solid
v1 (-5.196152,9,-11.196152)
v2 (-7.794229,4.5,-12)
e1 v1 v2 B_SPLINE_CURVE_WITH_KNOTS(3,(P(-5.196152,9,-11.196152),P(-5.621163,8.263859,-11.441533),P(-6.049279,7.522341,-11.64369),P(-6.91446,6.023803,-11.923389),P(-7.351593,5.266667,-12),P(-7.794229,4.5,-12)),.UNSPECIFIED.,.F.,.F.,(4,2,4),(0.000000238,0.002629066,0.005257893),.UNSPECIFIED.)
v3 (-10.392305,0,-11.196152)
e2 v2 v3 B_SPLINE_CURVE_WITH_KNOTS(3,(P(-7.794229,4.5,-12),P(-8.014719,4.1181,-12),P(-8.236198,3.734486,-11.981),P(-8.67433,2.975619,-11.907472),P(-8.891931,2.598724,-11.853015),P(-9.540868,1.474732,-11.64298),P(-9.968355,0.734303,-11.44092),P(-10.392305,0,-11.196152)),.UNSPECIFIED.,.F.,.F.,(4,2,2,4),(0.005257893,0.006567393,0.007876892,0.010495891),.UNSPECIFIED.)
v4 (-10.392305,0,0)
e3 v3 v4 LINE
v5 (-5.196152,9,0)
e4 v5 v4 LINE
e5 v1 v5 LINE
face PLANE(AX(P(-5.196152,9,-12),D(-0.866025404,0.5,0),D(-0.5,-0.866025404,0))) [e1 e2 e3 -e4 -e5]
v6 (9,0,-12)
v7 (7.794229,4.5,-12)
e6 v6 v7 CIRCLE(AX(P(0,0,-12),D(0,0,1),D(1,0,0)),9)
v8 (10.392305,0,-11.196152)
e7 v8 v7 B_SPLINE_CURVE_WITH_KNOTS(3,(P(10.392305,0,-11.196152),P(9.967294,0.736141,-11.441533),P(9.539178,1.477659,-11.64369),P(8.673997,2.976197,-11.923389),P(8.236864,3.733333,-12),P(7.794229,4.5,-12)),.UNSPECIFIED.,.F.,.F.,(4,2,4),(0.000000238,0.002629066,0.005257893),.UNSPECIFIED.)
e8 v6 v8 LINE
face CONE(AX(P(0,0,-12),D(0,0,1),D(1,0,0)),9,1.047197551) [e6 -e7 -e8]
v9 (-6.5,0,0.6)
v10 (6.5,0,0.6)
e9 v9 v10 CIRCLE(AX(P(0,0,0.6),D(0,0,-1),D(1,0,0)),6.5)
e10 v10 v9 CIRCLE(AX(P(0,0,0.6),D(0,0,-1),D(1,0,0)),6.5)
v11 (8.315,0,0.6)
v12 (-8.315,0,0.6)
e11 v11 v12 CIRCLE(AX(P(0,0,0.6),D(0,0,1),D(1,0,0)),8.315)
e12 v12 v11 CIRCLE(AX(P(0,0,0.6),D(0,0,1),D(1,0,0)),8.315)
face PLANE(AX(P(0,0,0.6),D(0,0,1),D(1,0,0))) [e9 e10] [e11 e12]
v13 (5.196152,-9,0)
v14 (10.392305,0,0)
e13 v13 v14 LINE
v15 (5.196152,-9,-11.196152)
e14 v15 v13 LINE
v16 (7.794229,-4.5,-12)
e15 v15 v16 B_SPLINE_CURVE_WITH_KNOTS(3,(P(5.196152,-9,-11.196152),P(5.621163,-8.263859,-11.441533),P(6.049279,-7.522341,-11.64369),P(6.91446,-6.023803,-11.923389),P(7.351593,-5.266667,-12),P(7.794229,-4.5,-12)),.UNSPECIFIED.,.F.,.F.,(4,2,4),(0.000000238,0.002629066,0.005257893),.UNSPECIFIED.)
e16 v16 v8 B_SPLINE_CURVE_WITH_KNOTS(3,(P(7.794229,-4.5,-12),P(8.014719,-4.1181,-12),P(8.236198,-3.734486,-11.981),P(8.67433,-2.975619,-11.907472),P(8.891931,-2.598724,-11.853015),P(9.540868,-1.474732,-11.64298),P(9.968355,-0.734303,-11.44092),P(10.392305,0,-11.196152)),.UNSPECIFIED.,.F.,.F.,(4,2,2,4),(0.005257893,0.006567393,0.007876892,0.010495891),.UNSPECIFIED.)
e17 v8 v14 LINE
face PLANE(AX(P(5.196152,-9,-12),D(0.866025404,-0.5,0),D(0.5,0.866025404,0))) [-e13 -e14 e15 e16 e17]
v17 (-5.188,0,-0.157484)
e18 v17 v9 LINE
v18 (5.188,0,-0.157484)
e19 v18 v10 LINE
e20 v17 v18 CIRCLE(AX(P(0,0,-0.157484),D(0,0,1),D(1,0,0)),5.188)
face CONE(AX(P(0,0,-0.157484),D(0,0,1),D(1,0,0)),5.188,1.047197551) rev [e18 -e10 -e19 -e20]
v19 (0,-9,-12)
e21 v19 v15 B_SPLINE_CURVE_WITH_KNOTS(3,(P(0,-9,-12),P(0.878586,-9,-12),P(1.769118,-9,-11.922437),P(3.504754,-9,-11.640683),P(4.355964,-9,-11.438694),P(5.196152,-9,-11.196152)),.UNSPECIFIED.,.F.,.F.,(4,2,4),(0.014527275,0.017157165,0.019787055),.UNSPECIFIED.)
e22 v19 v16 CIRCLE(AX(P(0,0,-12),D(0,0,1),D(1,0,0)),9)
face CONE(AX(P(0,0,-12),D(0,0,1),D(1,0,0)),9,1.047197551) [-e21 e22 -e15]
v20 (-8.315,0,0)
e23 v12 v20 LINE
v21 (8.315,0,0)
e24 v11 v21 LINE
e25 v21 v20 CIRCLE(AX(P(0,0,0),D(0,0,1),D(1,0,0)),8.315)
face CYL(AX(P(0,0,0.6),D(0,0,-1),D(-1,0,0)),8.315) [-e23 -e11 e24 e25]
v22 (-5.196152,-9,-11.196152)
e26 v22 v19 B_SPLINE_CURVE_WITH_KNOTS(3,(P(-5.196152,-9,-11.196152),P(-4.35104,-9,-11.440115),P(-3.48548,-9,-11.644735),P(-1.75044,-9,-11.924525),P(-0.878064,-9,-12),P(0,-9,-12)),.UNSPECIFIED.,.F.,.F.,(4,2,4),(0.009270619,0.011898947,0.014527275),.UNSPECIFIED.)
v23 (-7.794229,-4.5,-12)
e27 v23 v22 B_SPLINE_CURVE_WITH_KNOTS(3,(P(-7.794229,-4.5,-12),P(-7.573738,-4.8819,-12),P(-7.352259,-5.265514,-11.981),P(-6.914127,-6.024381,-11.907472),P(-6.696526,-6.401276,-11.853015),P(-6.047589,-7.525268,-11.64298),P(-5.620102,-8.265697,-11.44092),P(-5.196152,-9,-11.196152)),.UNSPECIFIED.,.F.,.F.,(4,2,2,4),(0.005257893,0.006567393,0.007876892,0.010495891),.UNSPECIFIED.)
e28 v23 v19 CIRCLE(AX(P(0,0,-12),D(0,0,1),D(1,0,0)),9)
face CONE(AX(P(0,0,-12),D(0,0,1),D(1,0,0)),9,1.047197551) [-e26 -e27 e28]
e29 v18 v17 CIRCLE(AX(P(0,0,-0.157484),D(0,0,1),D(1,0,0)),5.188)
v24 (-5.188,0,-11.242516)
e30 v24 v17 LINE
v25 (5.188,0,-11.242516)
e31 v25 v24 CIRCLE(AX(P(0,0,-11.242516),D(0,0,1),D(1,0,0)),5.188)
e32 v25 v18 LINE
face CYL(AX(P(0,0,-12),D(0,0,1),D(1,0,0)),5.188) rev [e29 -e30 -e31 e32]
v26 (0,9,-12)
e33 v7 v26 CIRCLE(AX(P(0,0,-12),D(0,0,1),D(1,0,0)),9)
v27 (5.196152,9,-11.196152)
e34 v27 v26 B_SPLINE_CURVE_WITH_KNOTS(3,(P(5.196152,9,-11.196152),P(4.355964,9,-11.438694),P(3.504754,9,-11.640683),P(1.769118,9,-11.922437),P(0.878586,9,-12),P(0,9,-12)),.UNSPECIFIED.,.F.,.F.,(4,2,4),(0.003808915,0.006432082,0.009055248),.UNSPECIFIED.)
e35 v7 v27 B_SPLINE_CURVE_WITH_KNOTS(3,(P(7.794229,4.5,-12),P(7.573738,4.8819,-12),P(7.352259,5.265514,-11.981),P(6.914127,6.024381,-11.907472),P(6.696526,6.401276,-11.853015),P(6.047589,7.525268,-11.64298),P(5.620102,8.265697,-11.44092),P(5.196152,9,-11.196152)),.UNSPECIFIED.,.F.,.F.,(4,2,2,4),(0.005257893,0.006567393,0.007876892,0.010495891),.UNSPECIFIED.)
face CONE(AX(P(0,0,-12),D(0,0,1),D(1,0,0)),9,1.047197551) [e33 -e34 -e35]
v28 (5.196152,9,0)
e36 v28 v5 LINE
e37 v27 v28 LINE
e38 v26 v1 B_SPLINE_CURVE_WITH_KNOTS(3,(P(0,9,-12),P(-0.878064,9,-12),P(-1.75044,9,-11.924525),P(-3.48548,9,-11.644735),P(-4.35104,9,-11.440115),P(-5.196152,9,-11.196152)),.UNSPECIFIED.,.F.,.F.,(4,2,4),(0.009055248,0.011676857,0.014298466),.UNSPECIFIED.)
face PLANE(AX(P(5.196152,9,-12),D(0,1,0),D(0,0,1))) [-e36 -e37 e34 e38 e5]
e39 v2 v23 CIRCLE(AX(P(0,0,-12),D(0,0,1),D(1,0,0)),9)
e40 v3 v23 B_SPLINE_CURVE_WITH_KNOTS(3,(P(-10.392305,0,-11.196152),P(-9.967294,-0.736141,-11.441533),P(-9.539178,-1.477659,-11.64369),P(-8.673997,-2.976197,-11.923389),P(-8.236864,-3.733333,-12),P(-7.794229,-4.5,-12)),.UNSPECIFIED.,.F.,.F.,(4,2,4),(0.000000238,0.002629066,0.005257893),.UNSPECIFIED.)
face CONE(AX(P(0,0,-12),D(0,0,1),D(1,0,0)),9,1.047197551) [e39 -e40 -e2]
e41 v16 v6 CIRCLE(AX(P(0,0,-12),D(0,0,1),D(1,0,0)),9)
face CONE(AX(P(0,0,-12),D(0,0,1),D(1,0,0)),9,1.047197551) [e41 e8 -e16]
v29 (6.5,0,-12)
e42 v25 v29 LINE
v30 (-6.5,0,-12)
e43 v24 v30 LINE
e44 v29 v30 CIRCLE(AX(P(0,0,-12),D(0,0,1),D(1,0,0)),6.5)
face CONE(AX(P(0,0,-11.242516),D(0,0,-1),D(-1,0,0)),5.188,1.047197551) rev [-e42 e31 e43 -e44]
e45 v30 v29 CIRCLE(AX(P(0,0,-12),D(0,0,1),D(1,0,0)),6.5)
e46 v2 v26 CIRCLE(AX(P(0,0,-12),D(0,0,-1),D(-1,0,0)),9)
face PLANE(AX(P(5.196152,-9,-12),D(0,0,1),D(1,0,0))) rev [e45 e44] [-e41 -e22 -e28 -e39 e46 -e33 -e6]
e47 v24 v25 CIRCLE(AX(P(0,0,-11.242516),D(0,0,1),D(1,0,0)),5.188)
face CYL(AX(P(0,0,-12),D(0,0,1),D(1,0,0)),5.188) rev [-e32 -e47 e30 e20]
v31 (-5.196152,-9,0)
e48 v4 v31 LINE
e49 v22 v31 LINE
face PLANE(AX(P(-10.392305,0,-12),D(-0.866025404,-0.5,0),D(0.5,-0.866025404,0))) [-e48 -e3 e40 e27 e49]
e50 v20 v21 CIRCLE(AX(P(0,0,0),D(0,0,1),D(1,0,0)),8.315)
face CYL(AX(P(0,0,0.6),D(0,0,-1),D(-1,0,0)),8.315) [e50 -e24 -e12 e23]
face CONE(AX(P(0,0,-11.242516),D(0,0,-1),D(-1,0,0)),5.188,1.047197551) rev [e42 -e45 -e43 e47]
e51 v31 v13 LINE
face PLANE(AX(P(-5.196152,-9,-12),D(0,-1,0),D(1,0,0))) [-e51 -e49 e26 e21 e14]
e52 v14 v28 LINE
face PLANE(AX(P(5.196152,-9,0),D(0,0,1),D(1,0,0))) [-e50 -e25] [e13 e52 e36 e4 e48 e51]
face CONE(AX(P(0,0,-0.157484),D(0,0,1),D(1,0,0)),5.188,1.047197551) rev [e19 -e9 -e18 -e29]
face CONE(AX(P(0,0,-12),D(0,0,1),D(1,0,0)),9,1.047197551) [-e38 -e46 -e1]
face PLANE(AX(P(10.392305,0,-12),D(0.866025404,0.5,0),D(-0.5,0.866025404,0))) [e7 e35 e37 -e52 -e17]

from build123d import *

# Parameters (mm, degrees)
SKETCH1_R         = 5.188
BASENUT_DEPTH     = 12
EXTRUDE1_START    = 0.6
SKETCH3_R         = 8.315
SKETCH3_R_2       = 5.188
EXTRUDE1_DEPTH    = 0.6
ENDCHAMFER3_SIZE  = 1.312
ENDCHAMFER3_SIZE2 = 0.757483553


with BuildPart() as part:
    # Sketch1 → BaseNut (new body)
    with BuildSketch(Plane.XY):
        Polygon((5.196152423, -9), (10.392304845, 0), (5.196152423, 9), (-5.196152423, 9), (-10.392304845, 0), (-5.196152423, -9), align=None)
        Circle(SKETCH1_R, mode=Mode.SUBTRACT)
    extrude(amount=-BASENUT_DEPTH)

    # Sketch2 → Chamfer1 (revolve, cut)
    with BuildSketch(Plane(origin=(-16.706149795, 0, -15.04811501), x_dir=(0, 0, 1), z_dir=(0, 1, 0))):
        Polygon((3.04811501, 25.706149795), (3.04811501, 27.098454641), (3.851962587, 27.098454641), align=None)
    revolve(axis=Axis((0, 0, -38.770766557), (0, 0, 1)), mode=Mode.SUBTRACT)

    # Sketch6 → EndChamfer1 (revolve, cut)
    with BuildSketch(Plane(origin=(-9.197458863, 0, -10.252541137), x_dir=(0, 0, 1), z_dir=(0, 1, 0))):
        Polygon((-1.747458863, 14.385458863), (-1.747458863, 15.697458863), (-0.989975309, 14.385458863), align=None)
    revolve(axis=Axis((0, 0, 13.104863586), (0, 0, -1)), mode=Mode.SUBTRACT)

    # Sketch3 → Extrude1 (add)
    with BuildSketch(Plane(origin=(-18.48918612, 11.17895969, 0), x_dir=(1, 0, 0), z_dir=(0, 0, 1)).offset(EXTRUDE1_START)):
        with Locations((18.48918612, -11.17895969)):
            Circle(SKETCH3_R)
        with Locations((18.48918612, -11.17895969)):
            Circle(SKETCH3_R_2, mode=Mode.SUBTRACT)
    extrude(amount=-EXTRUDE1_DEPTH)

    # EndChamfer3
    endchamfer3_edges = [part.edges().sort_by_distance(p)[0] for p in [
        (-5.188, 0, 0.6),
    ]]
    endchamfer3_side = [part.faces().sort_by_distance(p)[0] for p in [
        (-8.079816285, 0, 0.6),
    ]]
    chamfer(endchamfer3_edges, length=ENDCHAMFER3_SIZE, length2=ENDCHAMFER3_SIZE2, reference=endchamfer3_side[0])


solid = part.part
